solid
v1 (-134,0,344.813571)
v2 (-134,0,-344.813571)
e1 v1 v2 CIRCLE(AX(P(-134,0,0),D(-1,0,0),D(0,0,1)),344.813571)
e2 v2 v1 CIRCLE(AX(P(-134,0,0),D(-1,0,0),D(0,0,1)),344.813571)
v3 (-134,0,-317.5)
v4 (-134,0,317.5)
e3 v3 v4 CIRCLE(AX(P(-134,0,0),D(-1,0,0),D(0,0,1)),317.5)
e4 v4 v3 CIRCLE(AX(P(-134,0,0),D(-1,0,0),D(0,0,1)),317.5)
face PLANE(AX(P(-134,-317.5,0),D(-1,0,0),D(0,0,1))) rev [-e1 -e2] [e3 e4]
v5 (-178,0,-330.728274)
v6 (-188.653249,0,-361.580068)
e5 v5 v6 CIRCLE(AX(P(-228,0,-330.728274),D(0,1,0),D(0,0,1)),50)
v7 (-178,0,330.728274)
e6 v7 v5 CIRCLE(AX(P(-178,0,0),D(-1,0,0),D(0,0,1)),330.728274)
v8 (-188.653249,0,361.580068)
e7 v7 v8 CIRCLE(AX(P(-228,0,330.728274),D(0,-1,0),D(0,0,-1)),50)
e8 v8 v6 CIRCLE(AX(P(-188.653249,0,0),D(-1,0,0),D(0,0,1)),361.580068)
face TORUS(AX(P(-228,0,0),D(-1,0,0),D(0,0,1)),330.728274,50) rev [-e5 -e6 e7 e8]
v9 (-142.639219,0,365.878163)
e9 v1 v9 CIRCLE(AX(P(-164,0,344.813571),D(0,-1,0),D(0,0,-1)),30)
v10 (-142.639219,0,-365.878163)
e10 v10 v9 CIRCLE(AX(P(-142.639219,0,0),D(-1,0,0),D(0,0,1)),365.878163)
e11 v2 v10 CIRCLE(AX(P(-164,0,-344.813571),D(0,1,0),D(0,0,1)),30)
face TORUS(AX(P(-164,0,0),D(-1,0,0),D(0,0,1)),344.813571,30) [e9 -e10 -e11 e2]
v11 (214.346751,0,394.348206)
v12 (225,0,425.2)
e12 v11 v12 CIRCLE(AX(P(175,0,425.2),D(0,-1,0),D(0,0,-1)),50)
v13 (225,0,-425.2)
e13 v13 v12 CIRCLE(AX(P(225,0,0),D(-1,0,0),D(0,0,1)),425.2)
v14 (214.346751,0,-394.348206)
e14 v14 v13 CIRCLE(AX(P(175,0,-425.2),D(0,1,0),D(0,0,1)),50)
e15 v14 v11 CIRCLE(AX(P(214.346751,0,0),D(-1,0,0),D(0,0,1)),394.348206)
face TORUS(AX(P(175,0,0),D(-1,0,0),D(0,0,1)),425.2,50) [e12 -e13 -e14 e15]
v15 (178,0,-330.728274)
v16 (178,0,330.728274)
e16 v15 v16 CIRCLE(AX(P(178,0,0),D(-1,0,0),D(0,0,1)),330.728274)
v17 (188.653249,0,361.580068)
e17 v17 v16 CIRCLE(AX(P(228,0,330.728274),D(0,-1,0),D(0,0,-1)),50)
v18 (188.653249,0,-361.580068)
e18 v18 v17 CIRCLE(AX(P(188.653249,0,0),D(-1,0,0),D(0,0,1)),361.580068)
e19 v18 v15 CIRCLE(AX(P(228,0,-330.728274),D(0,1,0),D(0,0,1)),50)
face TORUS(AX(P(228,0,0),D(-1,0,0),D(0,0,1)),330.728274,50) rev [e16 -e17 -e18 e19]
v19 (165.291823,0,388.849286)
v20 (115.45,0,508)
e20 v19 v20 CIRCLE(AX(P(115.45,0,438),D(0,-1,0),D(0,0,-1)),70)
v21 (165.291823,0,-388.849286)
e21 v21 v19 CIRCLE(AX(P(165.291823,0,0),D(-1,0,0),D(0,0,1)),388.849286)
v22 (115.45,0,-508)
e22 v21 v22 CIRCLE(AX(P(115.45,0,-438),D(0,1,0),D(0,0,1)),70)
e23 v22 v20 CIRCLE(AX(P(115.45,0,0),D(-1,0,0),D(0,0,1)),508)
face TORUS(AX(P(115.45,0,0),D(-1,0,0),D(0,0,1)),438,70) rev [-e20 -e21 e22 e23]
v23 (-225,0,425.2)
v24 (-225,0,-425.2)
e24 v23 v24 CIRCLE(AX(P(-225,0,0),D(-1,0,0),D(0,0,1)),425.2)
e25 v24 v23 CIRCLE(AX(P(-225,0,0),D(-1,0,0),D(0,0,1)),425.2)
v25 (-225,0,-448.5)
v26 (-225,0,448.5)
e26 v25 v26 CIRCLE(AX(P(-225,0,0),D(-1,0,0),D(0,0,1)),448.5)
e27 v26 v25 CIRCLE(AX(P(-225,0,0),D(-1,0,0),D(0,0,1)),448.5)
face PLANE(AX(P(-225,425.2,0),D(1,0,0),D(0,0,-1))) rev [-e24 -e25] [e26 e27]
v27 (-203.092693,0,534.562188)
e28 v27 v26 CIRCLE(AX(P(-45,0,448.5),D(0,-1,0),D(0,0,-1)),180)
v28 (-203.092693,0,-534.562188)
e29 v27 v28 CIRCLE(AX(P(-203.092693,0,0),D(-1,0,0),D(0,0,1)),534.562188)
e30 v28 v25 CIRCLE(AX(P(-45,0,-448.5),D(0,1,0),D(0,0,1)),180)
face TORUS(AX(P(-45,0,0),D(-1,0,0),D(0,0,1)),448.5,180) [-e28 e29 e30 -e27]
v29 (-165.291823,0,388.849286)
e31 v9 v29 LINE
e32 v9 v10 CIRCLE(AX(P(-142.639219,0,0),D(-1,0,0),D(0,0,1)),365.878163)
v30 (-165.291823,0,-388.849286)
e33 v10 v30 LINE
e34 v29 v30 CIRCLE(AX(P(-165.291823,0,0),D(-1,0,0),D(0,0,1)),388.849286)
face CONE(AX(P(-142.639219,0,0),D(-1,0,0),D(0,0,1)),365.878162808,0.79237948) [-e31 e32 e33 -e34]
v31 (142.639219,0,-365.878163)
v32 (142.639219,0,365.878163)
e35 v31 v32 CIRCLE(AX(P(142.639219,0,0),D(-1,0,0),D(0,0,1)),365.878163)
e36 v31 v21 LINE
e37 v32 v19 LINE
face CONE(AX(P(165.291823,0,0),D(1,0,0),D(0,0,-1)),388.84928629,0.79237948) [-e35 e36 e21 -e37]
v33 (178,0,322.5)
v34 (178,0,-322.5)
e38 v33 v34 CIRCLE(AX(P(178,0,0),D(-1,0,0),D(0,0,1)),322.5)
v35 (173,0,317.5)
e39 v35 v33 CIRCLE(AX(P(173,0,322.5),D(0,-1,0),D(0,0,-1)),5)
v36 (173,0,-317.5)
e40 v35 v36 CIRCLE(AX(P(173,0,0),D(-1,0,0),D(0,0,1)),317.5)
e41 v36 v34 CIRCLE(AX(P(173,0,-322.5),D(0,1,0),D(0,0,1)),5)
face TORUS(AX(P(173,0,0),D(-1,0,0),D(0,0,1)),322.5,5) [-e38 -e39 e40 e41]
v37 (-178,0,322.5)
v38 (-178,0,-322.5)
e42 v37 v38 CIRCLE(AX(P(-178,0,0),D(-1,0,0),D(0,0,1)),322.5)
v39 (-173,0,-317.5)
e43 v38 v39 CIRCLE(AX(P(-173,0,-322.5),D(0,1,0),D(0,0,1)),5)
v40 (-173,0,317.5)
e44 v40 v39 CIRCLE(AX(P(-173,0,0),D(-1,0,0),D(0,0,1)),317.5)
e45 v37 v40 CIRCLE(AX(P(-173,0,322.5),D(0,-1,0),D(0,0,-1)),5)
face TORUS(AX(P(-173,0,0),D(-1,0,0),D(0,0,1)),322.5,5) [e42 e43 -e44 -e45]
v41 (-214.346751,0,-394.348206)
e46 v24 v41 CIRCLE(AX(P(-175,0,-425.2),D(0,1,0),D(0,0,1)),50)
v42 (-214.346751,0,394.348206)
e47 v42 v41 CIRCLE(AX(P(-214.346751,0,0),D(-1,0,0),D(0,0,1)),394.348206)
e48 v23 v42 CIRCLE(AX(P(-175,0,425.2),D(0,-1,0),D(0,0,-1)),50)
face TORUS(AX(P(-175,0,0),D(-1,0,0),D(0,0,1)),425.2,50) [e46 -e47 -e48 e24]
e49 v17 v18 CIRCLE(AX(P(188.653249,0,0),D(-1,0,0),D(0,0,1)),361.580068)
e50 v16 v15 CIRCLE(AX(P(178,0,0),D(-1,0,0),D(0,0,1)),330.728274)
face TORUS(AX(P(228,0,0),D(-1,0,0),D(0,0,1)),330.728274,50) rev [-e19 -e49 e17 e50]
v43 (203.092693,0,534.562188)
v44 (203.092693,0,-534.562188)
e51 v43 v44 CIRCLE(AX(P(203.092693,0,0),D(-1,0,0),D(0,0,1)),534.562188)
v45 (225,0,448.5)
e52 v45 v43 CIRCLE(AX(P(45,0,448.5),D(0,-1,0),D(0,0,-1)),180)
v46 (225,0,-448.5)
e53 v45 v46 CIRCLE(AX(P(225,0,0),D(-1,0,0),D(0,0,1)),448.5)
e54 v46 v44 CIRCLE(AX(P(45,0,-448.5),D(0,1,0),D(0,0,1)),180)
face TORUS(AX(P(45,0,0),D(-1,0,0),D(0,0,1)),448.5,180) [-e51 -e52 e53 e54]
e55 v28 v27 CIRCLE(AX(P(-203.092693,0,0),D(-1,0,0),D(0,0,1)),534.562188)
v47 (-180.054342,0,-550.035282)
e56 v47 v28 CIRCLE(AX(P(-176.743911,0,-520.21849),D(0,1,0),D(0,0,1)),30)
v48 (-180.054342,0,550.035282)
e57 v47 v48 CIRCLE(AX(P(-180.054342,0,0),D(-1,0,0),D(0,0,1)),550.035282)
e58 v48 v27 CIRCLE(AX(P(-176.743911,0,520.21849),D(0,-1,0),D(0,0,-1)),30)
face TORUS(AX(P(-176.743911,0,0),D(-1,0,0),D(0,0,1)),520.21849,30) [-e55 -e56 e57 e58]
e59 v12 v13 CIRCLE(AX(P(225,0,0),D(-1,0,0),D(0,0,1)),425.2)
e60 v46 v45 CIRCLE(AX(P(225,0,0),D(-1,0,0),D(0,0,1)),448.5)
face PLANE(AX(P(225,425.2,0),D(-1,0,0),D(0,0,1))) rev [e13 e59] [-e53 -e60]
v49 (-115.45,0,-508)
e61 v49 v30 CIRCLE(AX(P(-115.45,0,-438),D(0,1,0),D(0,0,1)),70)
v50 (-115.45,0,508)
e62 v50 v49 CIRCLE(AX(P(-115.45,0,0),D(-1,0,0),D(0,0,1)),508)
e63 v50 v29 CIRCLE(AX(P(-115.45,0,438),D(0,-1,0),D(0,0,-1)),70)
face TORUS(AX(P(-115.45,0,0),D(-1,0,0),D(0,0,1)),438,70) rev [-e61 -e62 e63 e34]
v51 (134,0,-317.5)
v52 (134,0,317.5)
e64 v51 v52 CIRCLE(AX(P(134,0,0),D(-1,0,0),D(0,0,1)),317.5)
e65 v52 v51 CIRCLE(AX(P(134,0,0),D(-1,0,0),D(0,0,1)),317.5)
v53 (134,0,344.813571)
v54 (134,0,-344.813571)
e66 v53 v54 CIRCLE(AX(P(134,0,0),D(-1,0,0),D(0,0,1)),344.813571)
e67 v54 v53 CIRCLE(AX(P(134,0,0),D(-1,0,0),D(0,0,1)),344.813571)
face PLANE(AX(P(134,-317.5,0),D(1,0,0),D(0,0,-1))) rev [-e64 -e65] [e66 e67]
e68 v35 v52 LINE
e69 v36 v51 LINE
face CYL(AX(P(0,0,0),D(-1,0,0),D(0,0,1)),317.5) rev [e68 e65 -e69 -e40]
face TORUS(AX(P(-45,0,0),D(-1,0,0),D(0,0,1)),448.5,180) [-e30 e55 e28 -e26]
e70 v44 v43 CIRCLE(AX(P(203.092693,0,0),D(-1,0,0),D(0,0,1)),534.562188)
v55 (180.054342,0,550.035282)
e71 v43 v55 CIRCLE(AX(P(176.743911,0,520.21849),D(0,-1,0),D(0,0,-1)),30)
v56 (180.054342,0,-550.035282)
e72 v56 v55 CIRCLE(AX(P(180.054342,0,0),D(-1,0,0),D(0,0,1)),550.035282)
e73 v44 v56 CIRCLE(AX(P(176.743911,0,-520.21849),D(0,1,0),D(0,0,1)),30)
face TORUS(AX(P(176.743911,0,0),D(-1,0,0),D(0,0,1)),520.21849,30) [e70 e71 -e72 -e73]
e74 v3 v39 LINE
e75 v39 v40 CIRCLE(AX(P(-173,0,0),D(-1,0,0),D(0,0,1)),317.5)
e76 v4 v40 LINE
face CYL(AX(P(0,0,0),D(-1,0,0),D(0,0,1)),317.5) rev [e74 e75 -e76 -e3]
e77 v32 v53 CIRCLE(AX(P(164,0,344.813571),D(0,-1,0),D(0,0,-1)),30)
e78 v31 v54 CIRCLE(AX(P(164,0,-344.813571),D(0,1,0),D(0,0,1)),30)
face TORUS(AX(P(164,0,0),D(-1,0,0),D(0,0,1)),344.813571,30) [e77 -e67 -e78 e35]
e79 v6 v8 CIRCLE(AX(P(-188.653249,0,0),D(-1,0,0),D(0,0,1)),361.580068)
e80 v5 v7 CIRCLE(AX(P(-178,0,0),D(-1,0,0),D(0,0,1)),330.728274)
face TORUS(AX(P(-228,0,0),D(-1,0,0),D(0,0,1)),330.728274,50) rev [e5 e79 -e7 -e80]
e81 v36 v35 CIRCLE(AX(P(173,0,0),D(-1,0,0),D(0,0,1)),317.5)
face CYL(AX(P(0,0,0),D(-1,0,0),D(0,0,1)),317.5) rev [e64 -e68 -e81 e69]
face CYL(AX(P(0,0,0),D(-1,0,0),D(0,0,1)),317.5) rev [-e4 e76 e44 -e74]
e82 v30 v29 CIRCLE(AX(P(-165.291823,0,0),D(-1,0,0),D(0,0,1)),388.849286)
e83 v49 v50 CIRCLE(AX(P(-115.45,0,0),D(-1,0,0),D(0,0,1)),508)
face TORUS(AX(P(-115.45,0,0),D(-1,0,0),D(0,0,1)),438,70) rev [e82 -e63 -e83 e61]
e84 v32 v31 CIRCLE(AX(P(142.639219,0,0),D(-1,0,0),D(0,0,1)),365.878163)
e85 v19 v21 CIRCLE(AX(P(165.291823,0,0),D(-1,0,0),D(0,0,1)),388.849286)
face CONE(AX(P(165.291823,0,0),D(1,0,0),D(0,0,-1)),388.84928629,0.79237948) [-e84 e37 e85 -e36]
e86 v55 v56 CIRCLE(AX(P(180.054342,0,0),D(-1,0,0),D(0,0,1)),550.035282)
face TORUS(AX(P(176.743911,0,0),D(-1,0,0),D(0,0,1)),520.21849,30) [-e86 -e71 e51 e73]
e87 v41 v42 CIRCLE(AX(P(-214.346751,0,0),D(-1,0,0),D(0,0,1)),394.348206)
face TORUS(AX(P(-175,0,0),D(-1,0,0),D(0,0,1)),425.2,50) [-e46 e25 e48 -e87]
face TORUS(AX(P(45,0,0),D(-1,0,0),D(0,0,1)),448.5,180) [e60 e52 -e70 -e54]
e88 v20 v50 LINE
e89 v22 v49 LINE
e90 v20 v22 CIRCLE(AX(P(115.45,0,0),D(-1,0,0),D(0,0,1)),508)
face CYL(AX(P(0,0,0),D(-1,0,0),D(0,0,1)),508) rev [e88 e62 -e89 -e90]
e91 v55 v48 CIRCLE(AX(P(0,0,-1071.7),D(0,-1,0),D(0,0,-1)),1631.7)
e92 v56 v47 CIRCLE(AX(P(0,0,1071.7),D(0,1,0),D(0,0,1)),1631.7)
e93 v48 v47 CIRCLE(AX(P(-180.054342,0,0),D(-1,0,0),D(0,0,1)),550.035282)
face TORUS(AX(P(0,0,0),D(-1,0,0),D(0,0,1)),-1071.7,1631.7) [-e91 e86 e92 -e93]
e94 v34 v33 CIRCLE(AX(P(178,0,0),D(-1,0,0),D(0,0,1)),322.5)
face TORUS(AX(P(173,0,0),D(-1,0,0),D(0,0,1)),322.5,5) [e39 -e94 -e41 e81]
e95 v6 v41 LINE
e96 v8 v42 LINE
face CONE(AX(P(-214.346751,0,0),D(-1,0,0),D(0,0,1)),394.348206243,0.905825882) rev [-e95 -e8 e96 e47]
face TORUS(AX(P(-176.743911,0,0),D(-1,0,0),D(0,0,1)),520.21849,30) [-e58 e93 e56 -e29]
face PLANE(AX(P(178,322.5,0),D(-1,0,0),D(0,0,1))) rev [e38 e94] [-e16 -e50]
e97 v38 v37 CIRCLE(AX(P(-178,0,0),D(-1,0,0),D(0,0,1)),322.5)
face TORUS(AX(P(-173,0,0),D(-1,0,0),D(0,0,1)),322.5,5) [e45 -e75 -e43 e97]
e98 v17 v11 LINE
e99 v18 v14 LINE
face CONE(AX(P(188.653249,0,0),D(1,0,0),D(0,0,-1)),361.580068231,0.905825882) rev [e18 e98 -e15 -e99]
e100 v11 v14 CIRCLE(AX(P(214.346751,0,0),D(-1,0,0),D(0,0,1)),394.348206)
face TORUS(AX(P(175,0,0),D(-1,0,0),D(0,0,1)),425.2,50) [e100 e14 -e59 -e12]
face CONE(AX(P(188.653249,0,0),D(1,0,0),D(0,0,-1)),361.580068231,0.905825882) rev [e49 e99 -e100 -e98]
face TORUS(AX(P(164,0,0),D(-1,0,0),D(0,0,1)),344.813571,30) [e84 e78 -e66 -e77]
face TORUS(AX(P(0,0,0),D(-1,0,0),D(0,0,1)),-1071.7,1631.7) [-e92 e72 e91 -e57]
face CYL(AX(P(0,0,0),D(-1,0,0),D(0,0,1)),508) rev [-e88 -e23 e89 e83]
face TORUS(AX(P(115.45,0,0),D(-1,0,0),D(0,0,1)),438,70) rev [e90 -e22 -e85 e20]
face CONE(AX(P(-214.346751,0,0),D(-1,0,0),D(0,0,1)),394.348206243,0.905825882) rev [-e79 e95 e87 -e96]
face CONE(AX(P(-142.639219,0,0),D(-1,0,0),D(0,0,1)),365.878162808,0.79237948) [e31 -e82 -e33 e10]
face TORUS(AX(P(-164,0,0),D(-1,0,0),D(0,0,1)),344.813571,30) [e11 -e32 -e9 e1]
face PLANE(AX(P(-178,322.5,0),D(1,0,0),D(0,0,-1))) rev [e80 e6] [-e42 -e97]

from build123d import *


with BuildPart() as part:
    # 草图1 → 旋转1 (revolve)
    with BuildSketch(Plane.XY, mode=Mode.PRIVATE) as revolve_1_sk:
        with BuildLine():
            Line((-173, 317.5), (173, 317.5))
            ThreePointArc((173, 317.5), (176.535533906, 318.964466094), (178, 322.5))
            Line((178, 322.5), (178, 330.728274474))
            ThreePointArc((178, 330.728274474), (180.73829481, 347.047932024), (188.653248902, 361.580068231))
            Line((188.653248902, 361.580068231), (214.346751098, 394.348206243))
            ThreePointArc((214.346751098, 394.348206243), (222.26170519, 408.88034245), (225, 425.2))
            Line((225, 425.2), (225, 448.5))
            ThreePointArc((225, 448.5), (219.437216248, 492.903351085), (203.092693472, 534.562188392))
            ThreePointArc((203.092693472, 534.562188392), (193.47027923, 545.122879767), (180.054342229, 550.03528168))
            ThreePointArc((180.054342229, 550.03528168), (0, 560), (-180.054342229, 550.03528168))
            ThreePointArc((-180.054342229, 550.03528168), (-193.47027923, 545.122879767), (-203.092693472, 534.562188392))
            ThreePointArc((-203.092693472, 534.562188392), (-219.437216248, 492.903351085), (-225, 448.5))
            Line((-225, 448.5), (-225, 425.2))
            ThreePointArc((-225, 425.2), (-222.26170519, 408.88034245), (-214.346751098, 394.348206243))
            Line((-214.346751098, 394.348206243), (-188.653248902, 361.580068231))
            ThreePointArc((-188.653248902, 361.580068231), (-180.73829481, 347.047932024), (-178, 330.728274474))
            Line((-178, 330.728274474), (-178, 322.5))
            ThreePointArc((-178, 322.5), (-176.535533906, 318.964466094), (-173, 317.5))
        make_face()
    revolve(revolve_1_sk.sketch.rotate(Axis((0, 0, 0), (1, 0, 0)), 90), axis=Axis((0, 0, 0), (1, 0, 0)))

    # 草图3 → 切除-旋转1 (revolve, cut)
    with BuildSketch(Plane.XY, mode=Mode.PRIVATE) as cut_revolve_1_sk:
        with BuildLine():
            Line((-134, -317.5), (134, -317.5))
            Line((134, -317.5), (134, -344.813571218))
            ThreePointArc((134, -344.813571218), (136.243708448, -356.197256004), (142.63921862, -365.878162808))
            Line((142.63921862, -365.878162808), (165.291823219, -388.84928629))
            ThreePointArc((165.291823219, -388.84928629), (180.027666262, -465.013422963), (115.45, -508))
            Line((115.45, -508), (-115.45, -508))
            ThreePointArc((-115.45, -508), (-180.027666262, -465.013422963), (-165.291823219, -388.84928629))
            Line((-165.291823219, -388.84928629), (-142.63921862, -365.878162808))
            ThreePointArc((-142.63921862, -365.878162808), (-136.243708448, -356.197256004), (-134, -344.813571218))
            Line((-134, -344.813571218), (-134, -317.5))
        make_face()
    revolve(cut_revolve_1_sk.sketch.rotate(Axis((0, 0, 0), (1, 0, 0)), 270), axis=Axis((0, 0, 0), (1, 0, 0)), mode=Mode.SUBTRACT)


solid = part.part
